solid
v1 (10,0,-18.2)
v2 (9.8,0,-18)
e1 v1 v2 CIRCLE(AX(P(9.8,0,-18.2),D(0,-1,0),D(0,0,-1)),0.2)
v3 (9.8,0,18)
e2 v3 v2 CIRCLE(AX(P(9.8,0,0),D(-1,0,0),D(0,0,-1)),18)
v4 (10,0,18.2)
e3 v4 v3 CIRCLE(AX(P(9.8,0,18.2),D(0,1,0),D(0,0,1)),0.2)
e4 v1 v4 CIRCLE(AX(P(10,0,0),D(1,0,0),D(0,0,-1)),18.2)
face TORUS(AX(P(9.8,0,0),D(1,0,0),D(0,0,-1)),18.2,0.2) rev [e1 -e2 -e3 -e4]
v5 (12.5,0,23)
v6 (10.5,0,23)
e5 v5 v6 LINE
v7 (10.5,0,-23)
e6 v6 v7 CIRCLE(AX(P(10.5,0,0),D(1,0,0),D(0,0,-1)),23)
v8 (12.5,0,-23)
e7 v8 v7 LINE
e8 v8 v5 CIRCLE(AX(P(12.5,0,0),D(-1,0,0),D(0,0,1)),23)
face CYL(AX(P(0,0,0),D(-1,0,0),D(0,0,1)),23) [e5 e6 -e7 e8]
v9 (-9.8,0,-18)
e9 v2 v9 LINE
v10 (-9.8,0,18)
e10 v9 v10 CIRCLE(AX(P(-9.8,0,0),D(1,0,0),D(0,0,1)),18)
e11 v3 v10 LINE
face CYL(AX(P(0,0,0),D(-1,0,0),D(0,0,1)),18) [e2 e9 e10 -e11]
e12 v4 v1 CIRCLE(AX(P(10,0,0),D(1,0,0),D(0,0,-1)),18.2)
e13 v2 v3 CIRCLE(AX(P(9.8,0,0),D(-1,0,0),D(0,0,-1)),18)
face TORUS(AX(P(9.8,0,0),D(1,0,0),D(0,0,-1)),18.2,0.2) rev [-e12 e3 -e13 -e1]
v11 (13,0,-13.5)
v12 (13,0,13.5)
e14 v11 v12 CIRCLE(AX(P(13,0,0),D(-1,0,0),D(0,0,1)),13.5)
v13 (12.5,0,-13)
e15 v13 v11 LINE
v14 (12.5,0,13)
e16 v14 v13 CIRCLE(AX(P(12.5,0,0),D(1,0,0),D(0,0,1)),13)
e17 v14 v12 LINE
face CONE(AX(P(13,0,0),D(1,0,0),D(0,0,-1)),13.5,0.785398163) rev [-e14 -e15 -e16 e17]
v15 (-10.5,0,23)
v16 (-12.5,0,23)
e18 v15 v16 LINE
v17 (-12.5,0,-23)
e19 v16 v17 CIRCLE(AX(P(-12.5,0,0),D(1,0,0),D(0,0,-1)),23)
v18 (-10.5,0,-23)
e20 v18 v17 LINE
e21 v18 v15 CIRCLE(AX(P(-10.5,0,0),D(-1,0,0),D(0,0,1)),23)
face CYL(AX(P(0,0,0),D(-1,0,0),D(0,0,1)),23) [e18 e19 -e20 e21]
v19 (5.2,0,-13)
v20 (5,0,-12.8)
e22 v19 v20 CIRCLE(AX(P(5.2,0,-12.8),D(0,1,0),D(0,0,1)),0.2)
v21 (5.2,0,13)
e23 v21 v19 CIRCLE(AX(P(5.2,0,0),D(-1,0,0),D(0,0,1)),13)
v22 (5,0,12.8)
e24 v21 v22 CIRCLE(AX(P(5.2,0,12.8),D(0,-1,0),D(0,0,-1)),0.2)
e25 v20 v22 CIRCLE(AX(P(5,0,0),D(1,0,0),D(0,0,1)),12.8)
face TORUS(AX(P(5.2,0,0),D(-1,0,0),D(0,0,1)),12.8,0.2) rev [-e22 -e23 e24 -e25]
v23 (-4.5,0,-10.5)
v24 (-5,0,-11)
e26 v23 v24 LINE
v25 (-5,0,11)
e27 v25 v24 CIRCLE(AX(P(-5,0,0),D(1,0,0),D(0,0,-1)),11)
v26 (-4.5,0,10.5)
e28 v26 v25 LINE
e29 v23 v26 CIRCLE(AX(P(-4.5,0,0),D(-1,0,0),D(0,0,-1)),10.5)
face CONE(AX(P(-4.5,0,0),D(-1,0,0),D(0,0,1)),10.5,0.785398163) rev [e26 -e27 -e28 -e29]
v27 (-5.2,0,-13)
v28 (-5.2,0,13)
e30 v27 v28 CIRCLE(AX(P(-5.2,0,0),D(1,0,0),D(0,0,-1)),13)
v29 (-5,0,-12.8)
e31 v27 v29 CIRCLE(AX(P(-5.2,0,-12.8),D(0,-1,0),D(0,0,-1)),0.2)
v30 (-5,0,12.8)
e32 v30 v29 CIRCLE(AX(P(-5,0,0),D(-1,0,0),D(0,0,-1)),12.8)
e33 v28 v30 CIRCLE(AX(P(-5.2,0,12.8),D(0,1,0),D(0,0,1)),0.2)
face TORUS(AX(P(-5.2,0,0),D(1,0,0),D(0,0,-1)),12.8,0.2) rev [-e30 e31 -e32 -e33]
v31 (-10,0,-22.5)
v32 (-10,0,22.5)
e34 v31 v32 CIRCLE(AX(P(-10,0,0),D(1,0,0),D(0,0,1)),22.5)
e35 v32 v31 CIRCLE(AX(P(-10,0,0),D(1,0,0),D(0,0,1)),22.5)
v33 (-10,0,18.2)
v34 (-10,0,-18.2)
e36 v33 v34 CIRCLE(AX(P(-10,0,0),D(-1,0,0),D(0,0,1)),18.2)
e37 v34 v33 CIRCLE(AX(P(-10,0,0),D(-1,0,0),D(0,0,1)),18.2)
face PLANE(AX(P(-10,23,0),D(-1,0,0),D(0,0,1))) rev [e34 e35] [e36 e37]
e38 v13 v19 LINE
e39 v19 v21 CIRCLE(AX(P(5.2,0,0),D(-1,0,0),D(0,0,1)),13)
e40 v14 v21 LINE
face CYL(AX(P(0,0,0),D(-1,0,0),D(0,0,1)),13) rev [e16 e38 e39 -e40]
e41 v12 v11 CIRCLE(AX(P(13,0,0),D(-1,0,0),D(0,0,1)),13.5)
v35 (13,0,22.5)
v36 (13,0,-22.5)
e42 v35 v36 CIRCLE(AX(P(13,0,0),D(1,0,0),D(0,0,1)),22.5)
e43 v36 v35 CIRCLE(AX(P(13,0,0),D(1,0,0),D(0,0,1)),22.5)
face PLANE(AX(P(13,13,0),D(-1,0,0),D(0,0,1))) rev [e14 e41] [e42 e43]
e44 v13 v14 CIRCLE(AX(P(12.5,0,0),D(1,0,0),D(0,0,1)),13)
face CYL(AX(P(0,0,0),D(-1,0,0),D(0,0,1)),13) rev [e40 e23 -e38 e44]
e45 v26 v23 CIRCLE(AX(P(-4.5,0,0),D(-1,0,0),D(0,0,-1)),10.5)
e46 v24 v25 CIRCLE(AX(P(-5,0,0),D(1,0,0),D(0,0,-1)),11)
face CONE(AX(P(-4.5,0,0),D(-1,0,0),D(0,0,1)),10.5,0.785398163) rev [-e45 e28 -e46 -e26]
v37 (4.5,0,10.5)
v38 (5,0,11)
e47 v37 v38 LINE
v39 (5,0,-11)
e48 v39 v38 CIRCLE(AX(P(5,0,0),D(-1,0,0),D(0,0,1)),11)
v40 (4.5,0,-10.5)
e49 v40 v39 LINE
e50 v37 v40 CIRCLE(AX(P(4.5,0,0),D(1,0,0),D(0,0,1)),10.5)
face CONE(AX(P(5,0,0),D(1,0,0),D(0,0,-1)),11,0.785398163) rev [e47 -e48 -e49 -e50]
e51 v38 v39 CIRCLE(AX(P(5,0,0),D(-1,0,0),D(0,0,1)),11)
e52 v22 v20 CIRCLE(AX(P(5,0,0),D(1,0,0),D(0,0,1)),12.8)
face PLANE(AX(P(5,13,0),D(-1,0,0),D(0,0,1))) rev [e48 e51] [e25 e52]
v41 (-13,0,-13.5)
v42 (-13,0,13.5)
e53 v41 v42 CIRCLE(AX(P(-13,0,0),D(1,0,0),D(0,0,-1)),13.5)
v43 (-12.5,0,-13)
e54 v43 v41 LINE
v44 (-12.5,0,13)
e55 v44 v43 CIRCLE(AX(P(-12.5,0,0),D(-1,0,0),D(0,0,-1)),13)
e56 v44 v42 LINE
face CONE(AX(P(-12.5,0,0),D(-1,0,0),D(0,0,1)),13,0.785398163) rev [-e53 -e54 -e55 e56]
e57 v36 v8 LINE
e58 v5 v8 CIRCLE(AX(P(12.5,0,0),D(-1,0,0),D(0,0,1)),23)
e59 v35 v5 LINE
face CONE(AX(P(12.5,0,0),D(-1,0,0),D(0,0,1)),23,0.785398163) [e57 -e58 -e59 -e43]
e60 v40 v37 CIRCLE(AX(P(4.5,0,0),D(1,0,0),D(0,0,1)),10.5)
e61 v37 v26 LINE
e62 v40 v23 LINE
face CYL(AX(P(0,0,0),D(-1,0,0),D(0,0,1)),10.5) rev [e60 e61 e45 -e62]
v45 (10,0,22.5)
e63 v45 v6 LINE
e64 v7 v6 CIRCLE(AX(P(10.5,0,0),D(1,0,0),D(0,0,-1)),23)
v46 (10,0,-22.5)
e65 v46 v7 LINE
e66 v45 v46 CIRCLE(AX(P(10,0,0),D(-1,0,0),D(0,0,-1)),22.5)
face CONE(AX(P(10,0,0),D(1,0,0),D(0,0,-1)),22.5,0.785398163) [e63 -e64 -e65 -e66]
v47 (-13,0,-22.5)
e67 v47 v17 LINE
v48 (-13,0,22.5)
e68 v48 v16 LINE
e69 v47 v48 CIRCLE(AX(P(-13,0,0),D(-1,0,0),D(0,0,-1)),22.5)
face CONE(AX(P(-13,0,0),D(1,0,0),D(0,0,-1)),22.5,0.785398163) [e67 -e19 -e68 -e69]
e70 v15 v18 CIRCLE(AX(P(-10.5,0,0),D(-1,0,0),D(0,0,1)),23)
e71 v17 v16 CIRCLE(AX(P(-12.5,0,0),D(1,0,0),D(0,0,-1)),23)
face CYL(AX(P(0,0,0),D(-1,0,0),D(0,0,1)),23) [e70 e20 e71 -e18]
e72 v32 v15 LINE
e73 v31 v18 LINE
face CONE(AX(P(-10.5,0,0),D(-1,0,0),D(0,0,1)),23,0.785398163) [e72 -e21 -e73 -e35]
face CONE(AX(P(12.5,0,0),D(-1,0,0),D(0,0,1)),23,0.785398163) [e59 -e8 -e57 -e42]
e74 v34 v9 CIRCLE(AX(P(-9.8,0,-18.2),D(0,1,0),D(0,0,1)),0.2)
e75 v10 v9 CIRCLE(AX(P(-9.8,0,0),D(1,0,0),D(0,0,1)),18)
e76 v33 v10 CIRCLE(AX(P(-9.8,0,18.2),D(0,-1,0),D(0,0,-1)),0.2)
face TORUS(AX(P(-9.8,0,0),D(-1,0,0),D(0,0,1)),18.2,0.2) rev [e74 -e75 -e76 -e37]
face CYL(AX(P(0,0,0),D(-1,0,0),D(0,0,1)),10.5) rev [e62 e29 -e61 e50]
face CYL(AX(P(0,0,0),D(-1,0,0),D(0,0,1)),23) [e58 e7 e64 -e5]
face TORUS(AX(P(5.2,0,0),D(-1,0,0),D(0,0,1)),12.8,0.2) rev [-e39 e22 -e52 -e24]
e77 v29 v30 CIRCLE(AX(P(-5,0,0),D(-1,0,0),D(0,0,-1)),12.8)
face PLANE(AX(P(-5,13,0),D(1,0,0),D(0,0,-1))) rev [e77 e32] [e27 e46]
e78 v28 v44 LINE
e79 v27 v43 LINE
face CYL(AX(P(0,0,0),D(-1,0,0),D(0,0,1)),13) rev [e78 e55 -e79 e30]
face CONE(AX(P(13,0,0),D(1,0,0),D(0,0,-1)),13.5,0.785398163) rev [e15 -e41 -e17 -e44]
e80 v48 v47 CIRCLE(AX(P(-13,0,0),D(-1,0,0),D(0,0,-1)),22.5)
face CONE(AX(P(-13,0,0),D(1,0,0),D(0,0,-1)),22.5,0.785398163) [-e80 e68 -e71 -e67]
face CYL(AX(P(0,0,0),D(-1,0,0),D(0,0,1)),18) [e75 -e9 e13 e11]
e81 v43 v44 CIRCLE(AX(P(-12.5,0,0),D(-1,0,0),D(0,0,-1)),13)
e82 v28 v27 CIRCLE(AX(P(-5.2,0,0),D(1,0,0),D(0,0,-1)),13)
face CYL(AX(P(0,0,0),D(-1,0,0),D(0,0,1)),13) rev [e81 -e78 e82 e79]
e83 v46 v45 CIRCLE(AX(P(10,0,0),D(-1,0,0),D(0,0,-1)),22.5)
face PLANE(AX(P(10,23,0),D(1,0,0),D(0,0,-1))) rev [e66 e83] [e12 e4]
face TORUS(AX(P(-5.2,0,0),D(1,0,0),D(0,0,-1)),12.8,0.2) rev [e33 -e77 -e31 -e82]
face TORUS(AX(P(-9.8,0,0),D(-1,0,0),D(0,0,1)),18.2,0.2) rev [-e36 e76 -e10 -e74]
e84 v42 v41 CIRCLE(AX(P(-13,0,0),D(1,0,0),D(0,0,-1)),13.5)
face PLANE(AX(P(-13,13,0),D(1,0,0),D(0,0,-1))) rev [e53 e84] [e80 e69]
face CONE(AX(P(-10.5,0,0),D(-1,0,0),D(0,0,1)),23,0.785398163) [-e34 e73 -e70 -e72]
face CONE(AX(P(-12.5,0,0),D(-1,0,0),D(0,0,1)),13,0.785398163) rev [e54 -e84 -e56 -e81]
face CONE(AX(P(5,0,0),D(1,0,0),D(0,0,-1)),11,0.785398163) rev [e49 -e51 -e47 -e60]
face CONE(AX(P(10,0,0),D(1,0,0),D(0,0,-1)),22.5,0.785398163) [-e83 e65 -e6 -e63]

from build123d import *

# Parameters (mm, degrees)
CHAMFER_1_SIZE = 0.5
FILLET_1_R     = 0.2


with BuildPart() as part:
    # 草图1 → 旋转1 (revolve)
    with BuildSketch(Plane.XY, mode=Mode.PRIVATE) as revolve_1_sk:
        Polygon((-13, 13), (-13, 23), (-10, 23), (-10, 18), (10, 18), (10, 23), (13, 23), (13, 13), (5, 13), (5, 10.5), (-5, 10.5), (-5, 13), align=None)
    revolve(revolve_1_sk.sketch.rotate(Axis((0, 0, 0), (1, 0, 0)), 90), axis=Axis((0, 0, 0), (1, 0, 0)))

    # 倒角1
    chamfer_1_edges = [part.edges().sort_by_distance(p)[0] for p in [
        (13, 0, -13),
        (13, 0, -23),
        (10, 0, -23),
        (-10, 0, -23),
        (-13, 0, -23),
        (-13, 0, -13),
        (-5, 0, -10.5),
        (5, 0, -10.5),
    ]]
    chamfer(chamfer_1_edges, length=CHAMFER_1_SIZE)

    # 圆角1
    fillet_1_edges = [part.edges().sort_by_distance(p)[0] for p in [
        (10, 0, -18),
        (-10, 0, -18),
        (-5, 0, -13),
        (5, 0, -13),
    ]]
    fillet(fillet_1_edges, radius=FILLET_1_R)


solid = part.part
